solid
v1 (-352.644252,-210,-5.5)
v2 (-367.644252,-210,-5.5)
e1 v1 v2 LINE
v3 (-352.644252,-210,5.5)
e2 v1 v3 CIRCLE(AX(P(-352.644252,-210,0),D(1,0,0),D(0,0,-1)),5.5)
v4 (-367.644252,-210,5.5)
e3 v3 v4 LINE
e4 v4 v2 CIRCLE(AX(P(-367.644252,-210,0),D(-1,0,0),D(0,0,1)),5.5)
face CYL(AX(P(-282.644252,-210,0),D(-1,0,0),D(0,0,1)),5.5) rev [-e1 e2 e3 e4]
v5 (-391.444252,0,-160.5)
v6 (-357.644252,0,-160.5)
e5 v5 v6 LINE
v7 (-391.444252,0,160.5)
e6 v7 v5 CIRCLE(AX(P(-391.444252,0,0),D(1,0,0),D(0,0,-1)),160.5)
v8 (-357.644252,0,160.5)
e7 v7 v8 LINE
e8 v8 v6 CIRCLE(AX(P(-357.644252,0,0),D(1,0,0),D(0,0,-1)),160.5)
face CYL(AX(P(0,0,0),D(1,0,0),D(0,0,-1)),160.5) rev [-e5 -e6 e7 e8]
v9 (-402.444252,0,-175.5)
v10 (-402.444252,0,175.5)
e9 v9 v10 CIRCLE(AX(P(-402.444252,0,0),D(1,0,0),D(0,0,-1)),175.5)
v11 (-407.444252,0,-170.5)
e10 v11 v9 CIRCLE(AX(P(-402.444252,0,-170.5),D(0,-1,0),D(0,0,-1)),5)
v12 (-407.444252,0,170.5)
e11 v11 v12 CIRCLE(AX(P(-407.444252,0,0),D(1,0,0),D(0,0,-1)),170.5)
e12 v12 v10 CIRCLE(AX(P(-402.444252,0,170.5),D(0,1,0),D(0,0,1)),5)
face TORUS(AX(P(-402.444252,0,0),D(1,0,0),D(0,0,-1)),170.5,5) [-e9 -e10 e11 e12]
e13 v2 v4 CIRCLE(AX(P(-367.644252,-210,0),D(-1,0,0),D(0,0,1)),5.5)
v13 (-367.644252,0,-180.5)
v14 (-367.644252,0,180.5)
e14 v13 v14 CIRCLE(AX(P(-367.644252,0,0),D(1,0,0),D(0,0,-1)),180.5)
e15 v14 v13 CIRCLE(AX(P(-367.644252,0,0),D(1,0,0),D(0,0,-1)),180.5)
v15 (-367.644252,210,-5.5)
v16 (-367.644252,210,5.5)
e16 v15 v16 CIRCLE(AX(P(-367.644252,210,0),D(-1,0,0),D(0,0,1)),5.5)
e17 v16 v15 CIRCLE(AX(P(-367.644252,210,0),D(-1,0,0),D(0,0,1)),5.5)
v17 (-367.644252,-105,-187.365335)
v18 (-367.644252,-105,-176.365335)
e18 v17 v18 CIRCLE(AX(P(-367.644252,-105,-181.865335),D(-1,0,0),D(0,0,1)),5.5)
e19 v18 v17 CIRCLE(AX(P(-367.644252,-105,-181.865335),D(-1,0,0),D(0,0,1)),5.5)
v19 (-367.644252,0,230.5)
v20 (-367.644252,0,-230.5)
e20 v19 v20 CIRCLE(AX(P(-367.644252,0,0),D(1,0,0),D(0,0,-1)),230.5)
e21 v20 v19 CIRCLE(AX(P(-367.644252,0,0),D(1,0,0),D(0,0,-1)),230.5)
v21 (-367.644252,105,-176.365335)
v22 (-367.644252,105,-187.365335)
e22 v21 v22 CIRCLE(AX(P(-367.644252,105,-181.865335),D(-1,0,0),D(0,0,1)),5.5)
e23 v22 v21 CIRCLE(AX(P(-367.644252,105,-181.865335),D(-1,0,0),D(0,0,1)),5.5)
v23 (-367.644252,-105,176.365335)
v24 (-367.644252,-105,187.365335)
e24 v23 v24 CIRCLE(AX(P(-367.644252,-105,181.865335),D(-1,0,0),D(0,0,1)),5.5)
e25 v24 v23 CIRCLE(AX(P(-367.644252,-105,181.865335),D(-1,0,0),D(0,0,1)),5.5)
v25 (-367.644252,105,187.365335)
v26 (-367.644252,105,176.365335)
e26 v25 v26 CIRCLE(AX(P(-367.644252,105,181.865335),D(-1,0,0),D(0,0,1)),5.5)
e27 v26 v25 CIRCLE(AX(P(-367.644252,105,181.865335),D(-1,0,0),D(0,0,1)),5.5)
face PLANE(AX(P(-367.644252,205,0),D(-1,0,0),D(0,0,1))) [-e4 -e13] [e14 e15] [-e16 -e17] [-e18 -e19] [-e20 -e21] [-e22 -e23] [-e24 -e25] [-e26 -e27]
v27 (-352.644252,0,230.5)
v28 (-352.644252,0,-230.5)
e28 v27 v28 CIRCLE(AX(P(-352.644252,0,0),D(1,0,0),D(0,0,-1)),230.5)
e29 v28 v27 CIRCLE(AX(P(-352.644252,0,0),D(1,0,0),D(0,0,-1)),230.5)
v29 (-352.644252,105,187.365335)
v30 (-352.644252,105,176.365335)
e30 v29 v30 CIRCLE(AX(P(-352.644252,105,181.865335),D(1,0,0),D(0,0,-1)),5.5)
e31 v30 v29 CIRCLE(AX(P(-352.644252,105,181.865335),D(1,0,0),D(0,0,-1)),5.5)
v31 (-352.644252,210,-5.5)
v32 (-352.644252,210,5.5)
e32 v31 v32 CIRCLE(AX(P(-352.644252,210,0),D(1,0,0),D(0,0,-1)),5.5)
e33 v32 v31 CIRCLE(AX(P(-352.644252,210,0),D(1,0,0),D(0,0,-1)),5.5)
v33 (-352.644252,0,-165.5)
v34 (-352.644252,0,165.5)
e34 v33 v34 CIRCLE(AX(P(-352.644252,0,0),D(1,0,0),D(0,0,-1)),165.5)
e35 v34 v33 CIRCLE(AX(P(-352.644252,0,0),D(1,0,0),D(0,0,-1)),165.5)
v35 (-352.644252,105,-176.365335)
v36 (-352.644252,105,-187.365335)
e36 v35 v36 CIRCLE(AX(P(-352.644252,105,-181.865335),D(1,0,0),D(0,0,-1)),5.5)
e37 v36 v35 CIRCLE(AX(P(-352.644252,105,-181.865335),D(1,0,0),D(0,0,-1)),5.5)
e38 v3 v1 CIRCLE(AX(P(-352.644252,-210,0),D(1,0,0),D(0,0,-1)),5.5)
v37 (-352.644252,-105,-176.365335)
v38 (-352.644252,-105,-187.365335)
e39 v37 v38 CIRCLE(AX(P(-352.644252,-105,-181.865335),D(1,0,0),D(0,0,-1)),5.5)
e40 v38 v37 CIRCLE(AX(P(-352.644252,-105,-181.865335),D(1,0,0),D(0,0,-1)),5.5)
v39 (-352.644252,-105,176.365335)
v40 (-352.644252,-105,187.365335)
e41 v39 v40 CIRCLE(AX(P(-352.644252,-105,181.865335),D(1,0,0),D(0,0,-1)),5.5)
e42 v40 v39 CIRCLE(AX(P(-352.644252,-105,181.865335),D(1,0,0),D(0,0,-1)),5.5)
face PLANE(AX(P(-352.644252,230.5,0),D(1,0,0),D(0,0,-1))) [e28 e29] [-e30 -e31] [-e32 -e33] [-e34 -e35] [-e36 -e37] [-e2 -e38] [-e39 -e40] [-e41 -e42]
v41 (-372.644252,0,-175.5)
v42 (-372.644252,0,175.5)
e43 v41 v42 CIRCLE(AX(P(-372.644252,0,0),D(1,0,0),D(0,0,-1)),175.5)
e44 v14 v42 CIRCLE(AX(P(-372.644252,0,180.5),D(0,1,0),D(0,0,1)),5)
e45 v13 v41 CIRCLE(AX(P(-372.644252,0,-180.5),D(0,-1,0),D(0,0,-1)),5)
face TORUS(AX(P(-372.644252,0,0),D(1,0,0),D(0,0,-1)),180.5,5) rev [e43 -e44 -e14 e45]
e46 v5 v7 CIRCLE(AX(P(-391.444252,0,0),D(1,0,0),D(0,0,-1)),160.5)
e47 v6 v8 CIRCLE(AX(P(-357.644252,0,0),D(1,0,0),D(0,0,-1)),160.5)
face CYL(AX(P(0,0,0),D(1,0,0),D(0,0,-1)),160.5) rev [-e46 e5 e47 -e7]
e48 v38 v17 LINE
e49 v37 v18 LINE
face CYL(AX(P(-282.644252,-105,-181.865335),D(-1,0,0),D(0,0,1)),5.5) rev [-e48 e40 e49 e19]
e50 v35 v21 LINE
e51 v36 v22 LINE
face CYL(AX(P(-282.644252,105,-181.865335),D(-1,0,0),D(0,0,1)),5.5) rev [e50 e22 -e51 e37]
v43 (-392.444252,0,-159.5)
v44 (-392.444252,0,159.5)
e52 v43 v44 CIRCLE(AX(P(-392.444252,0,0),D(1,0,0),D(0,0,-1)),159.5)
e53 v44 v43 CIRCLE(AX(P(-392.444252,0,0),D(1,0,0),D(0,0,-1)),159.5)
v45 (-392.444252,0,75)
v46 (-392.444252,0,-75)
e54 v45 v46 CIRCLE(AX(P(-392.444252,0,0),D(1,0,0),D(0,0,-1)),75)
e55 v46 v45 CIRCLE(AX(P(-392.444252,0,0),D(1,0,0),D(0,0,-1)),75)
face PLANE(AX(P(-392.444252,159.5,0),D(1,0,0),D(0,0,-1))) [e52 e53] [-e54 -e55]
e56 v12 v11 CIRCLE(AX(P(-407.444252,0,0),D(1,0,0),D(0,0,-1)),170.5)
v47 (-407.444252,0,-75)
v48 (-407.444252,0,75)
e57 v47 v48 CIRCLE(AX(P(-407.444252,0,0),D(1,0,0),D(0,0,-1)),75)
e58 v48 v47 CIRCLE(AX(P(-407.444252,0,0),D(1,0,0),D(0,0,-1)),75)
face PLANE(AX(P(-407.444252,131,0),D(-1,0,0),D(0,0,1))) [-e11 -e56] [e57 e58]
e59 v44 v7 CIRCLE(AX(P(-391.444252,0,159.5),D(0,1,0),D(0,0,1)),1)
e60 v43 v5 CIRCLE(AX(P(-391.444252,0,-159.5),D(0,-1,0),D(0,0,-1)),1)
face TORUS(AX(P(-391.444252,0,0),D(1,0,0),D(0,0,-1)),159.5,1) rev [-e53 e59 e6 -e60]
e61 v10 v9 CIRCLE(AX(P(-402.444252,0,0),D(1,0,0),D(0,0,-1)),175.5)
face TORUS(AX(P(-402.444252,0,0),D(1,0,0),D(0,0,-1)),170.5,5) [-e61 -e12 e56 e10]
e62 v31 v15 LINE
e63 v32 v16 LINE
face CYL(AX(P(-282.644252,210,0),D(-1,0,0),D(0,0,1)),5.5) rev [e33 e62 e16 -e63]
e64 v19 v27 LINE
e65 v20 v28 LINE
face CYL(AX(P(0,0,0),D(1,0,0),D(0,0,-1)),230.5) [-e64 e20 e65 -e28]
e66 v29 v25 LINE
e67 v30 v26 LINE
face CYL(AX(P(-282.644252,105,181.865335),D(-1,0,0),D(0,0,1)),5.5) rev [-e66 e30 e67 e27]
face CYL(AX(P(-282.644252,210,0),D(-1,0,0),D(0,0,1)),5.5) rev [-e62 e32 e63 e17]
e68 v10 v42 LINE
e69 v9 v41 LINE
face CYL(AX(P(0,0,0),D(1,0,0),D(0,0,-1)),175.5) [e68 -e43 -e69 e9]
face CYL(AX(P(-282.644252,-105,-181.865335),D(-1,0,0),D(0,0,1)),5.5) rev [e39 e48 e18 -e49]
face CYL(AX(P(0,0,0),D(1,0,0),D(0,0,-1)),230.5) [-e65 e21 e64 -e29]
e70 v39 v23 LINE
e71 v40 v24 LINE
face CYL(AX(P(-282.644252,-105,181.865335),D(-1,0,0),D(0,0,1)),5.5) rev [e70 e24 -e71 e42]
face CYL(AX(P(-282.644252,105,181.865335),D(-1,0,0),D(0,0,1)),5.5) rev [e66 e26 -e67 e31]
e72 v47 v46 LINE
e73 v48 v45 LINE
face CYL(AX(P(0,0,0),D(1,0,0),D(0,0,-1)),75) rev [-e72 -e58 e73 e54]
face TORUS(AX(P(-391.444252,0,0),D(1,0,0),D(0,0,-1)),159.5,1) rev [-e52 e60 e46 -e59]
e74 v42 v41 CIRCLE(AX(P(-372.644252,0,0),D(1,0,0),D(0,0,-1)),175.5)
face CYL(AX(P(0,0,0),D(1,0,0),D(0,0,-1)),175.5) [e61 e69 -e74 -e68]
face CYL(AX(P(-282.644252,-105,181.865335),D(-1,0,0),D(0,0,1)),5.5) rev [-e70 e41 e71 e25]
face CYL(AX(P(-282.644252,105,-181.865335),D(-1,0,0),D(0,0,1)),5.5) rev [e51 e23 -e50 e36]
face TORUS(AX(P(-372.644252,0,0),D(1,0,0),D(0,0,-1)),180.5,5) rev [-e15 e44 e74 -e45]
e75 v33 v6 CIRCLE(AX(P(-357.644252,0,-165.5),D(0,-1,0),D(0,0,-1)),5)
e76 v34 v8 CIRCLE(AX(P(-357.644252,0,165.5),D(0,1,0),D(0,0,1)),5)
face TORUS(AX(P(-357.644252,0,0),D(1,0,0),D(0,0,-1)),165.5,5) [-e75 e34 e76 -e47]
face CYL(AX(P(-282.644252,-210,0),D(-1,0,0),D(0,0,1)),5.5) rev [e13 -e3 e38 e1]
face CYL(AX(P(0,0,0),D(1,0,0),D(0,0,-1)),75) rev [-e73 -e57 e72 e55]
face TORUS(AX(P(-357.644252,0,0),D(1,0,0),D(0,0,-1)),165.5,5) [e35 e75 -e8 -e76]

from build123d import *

# Parameters (mm, degrees)
SKETCH2_R          = 5.5
CUT_EXTRUDE1_DEPTH = 85


with BuildPart() as part:
    # Sketch1 → Revolve1 (revolve)
    with BuildSketch(Plane.XY, mode=Mode.PRIVATE) as revolve1_sk:
        with BuildLine():
            Line((-357.644251927, 160.5), (-391.444251927, 160.5))
            ThreePointArc((-391.444251927, 160.5), (-392.151358708, 160.207106781), (-392.444251927, 159.5))
            Line((-392.444251927, 159.5), (-392.444251927, 131))
            Line((-392.444251927, 131), (-392.444251927, 75))
            Line((-392.444251927, 75), (-407.444251927, 75))
            Line((-407.444251927, 75), (-407.444251927, 131))
            Line((-407.444251927, 131), (-407.444251927, 170.5))
            ThreePointArc((-407.444251927, 170.5), (-405.979785833, 174.035533906), (-402.444251927, 175.5))
            Line((-402.444251927, 175.5), (-372.644251927, 175.5))
            ThreePointArc((-372.644251927, 175.5), (-369.108718021, 176.964466094), (-367.644251927, 180.5))
            Line((-367.644251927, 180.5), (-367.644251927, 205))
            Line((-367.644251927, 205), (-367.644251927, 230.5))
            Line((-367.644251927, 230.5), (-352.644251927, 230.5))
            Line((-352.644251927, 230.5), (-352.644251927, 205.5))
            Line((-352.644251927, 205.5), (-352.644251927, 165.5))
            ThreePointArc((-352.644251927, 165.5), (-354.108718021, 161.964466094), (-357.644251927, 160.5))
        make_face()
    revolve(revolve1_sk.sketch.rotate(Axis((0, 0, 0), (-1, 0, 0)), 90), axis=Axis((0, 0, 0), (-1, 0, 0)))

    # Sketch2 → Cut-Extrude1 (cut)
    with BuildSketch(Plane.ZY.offset(367.644251927)):
        with Locations((0, 210)):
            Circle(SKETCH2_R)
        with Locations((181.865334795, 105)):
            Circle(SKETCH2_R)
        with Locations((181.865334795, -105)):
            Circle(SKETCH2_R)
        with Locations((0, -210)):
            Circle(SKETCH2_R)
        with Locations((-181.865334795, -105)):
            Circle(SKETCH2_R)
        with Locations((-181.865334795, 105)):
            Circle(SKETCH2_R)
    extrude(amount=-CUT_EXTRUDE1_DEPTH, mode=Mode.SUBTRACT)


solid = part.part
